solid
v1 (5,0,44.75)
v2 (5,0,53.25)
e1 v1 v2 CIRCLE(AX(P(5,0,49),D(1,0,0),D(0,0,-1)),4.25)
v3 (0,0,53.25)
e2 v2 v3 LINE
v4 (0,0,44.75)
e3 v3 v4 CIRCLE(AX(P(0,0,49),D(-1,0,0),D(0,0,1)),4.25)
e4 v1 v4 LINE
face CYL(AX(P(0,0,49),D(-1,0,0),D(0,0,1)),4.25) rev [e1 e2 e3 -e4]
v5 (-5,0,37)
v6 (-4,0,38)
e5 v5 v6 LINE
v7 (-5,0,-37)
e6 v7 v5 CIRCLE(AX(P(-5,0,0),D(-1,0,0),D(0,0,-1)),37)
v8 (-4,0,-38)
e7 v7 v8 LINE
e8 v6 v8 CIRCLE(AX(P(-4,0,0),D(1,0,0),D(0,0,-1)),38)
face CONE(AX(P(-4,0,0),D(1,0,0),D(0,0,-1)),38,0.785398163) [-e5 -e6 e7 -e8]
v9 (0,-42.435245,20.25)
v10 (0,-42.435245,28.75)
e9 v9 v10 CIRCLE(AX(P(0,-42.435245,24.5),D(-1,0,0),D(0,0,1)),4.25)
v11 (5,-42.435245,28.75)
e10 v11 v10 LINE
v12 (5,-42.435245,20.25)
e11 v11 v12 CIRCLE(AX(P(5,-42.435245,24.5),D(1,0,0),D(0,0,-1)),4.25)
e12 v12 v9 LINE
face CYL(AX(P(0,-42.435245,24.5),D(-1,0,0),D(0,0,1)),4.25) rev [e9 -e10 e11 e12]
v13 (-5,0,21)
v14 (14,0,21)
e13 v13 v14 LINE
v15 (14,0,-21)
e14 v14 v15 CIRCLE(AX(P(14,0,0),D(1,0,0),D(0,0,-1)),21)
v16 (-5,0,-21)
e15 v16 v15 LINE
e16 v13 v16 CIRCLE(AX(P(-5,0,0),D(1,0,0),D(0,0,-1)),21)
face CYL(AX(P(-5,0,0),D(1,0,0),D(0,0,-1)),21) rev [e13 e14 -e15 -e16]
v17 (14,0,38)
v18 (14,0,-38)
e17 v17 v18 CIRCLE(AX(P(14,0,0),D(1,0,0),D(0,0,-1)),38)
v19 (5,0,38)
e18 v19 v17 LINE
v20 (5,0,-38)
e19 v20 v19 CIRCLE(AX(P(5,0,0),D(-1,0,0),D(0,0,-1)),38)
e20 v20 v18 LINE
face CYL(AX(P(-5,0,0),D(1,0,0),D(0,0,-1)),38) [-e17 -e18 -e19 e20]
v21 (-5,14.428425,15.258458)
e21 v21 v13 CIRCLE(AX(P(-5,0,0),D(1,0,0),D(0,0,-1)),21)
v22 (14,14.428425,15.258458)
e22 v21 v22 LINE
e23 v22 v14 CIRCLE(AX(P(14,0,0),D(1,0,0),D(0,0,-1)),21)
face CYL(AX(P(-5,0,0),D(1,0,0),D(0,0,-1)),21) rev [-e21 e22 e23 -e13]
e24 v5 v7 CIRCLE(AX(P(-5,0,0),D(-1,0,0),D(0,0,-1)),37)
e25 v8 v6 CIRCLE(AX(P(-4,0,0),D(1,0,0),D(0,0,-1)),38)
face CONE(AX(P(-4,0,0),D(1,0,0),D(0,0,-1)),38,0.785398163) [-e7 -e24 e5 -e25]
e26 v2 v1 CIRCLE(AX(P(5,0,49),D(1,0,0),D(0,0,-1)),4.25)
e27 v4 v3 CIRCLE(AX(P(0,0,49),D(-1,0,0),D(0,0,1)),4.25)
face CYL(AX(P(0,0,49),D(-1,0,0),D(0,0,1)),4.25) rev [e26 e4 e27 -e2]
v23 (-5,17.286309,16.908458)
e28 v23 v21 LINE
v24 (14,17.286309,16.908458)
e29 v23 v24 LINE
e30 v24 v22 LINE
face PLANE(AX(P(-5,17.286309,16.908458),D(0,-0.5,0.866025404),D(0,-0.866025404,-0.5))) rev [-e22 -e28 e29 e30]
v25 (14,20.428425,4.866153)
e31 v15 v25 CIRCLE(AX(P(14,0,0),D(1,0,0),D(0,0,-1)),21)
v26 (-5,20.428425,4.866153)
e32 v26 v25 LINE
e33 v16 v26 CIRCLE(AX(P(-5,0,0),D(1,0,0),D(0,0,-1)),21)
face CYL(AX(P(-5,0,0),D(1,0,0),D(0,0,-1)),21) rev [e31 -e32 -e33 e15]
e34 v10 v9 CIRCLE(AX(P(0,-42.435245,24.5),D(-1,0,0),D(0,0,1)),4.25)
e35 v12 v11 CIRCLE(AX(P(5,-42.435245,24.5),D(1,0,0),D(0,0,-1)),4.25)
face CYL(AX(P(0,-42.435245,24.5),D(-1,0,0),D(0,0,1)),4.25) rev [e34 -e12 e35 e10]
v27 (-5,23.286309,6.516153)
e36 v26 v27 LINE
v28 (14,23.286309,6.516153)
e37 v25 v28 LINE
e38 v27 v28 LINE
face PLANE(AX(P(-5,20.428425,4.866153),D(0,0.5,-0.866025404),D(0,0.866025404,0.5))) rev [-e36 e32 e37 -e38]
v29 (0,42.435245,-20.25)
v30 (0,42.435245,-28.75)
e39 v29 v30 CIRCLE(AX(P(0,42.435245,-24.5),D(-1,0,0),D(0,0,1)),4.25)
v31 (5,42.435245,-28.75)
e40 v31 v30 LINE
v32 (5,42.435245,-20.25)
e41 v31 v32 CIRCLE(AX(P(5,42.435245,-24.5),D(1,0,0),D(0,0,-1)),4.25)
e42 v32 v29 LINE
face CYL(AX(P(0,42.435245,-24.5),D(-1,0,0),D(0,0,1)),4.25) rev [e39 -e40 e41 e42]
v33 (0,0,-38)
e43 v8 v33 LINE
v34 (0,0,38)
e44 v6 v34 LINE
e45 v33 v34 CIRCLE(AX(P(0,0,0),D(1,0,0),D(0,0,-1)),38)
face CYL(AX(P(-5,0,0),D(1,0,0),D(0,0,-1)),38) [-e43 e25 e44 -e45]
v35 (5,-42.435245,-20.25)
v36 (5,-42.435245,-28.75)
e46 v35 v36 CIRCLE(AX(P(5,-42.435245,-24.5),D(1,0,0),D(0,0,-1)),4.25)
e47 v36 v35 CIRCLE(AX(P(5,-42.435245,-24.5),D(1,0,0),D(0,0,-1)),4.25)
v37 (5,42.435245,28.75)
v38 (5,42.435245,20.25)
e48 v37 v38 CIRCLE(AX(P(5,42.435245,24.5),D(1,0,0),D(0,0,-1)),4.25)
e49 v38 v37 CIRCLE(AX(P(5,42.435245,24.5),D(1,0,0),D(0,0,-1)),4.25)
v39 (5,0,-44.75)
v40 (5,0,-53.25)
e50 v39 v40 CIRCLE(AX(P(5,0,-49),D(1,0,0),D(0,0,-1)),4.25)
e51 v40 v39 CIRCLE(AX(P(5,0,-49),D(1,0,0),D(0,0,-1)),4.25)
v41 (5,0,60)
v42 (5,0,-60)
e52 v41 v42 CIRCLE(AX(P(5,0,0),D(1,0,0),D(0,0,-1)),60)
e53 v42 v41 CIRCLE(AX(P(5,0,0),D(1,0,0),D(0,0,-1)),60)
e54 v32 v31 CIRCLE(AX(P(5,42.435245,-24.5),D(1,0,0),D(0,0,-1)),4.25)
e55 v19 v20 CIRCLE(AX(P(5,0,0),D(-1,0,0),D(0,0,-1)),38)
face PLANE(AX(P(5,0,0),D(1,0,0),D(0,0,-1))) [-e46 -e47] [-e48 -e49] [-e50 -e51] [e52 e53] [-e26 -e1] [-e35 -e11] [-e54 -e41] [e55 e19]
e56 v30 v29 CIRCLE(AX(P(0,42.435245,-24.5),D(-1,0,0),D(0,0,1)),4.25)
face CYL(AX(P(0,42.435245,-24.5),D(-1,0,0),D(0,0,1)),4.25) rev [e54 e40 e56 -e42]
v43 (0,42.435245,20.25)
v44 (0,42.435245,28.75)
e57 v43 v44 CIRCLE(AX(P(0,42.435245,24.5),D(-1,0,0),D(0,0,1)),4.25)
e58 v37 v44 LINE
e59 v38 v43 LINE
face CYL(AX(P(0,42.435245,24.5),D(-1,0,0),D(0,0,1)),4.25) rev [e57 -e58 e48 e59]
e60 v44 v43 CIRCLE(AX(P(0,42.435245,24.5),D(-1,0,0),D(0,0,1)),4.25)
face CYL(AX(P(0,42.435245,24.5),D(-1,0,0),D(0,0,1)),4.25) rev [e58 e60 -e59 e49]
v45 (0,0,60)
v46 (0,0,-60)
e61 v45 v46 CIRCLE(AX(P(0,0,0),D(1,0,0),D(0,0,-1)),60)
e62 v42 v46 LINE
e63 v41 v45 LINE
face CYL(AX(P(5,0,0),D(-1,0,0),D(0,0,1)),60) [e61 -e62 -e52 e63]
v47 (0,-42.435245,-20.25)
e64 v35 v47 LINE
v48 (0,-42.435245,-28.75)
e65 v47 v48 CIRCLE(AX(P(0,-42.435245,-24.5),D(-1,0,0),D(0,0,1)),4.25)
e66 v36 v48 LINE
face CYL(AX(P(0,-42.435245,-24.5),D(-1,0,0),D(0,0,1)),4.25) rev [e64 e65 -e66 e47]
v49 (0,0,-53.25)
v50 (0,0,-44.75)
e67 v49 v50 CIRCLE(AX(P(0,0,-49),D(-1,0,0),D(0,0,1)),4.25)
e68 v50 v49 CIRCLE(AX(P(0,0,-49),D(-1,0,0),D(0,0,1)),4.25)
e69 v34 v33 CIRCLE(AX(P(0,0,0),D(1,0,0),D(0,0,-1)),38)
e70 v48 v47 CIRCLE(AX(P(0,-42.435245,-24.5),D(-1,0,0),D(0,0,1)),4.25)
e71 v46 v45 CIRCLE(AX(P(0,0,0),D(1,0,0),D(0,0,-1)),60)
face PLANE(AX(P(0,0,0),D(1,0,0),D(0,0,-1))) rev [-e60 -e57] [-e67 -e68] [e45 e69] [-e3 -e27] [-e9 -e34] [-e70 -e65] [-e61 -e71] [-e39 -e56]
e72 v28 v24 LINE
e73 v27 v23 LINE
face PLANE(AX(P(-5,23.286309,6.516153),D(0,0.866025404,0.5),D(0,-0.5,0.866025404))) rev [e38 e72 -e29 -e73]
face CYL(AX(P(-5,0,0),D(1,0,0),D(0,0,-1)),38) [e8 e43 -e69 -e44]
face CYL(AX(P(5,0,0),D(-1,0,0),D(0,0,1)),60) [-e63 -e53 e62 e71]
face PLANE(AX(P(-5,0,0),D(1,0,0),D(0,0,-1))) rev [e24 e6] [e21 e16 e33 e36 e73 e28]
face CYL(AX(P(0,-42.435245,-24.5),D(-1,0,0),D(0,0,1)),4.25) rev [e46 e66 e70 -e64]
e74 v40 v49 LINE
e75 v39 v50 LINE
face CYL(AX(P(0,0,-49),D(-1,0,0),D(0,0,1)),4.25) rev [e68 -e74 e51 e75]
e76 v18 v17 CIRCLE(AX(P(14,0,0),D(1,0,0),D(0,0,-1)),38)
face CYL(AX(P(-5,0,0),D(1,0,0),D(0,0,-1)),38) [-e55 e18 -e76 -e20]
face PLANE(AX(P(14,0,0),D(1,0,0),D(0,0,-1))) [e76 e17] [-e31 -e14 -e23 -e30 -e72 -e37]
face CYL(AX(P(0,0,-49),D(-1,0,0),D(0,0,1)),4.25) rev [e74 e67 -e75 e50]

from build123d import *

# Parameters (mm, degrees)
EXTRUDE_1_DEPTH         = 14
EXTRUDE_1_DEPTH_BACK    = 5
SKETCH_1_R              = 38
SKETCH_2_R              = 60
SKETCH_2_R_2            = 38
EXTRUDE_2_DEPTH         = 5
CHAMFER_1_SIZE          = 1
HOLE_WIZARD_M10_1_D     = 8.5
HOLE_WIZARD_M10_1_DEPTH = 24.5
HOLE_WIZARD_M10_1_TIP   = 2.553657631


with BuildPart() as part:
    # 草图1 → 凸台-拉伸1 (new, two sides: drawn at the far end of the back side and taken through both)
    with BuildSketch(Plane(origin=(0, 0, 0), x_dir=(0, 0, -1), z_dir=(1, 0, 0)).offset(-EXTRUDE_1_DEPTH_BACK)):
        Circle(SKETCH_1_R)
        with BuildLine():
            Line((-4.866153476, 20.428425058), (-6.516153476, 23.28630889))
            Line((-6.516153476, 23.28630889), (-16.908458321, 17.28630889))
            Line((-16.908458321, 17.28630889), (-15.258458321, 14.428425058))
            ThreePointArc((-15.258458321, 14.428425058), (10.5, -18.186533479), (-4.866153476, 20.428425058))
        make_face(mode=Mode.SUBTRACT)
    extrude(amount=EXTRUDE_1_DEPTH + EXTRUDE_1_DEPTH_BACK)

    # 草图2 → 凸台-拉伸2 (add)
    with BuildSketch(Plane(origin=(0, 0, 0), x_dir=(0, 0, -1), z_dir=(1, 0, 0))):
        Circle(SKETCH_2_R)
        Circle(SKETCH_2_R_2, mode=Mode.SUBTRACT)
    extrude(amount=EXTRUDE_2_DEPTH)

    # 倒角1
    chamfer_1_edges = [part.edges().sort_by_distance(p)[0] for p in [
        (-5, 0, 38),
    ]]
    chamfer(chamfer_1_edges, length=CHAMFER_1_SIZE)

    # M10 螺纹孔1
    with Locations(Plane.ZY):
        with Locations((24.5, 42.435244785), (49, 0), (24.5, -42.435244785), (-24.5, -42.435244785), (-49, 0), (-24.5, 42.435244785)):
            Hole(HOLE_WIZARD_M10_1_D / 2, depth=HOLE_WIZARD_M10_1_DEPTH)
            with Locations((0, 0, -(HOLE_WIZARD_M10_1_DEPTH + HOLE_WIZARD_M10_1_TIP / 2))):  # 118° drill point
                Cone(0, HOLE_WIZARD_M10_1_D / 2, HOLE_WIZARD_M10_1_TIP, mode=Mode.SUBTRACT)


solid = part.part
